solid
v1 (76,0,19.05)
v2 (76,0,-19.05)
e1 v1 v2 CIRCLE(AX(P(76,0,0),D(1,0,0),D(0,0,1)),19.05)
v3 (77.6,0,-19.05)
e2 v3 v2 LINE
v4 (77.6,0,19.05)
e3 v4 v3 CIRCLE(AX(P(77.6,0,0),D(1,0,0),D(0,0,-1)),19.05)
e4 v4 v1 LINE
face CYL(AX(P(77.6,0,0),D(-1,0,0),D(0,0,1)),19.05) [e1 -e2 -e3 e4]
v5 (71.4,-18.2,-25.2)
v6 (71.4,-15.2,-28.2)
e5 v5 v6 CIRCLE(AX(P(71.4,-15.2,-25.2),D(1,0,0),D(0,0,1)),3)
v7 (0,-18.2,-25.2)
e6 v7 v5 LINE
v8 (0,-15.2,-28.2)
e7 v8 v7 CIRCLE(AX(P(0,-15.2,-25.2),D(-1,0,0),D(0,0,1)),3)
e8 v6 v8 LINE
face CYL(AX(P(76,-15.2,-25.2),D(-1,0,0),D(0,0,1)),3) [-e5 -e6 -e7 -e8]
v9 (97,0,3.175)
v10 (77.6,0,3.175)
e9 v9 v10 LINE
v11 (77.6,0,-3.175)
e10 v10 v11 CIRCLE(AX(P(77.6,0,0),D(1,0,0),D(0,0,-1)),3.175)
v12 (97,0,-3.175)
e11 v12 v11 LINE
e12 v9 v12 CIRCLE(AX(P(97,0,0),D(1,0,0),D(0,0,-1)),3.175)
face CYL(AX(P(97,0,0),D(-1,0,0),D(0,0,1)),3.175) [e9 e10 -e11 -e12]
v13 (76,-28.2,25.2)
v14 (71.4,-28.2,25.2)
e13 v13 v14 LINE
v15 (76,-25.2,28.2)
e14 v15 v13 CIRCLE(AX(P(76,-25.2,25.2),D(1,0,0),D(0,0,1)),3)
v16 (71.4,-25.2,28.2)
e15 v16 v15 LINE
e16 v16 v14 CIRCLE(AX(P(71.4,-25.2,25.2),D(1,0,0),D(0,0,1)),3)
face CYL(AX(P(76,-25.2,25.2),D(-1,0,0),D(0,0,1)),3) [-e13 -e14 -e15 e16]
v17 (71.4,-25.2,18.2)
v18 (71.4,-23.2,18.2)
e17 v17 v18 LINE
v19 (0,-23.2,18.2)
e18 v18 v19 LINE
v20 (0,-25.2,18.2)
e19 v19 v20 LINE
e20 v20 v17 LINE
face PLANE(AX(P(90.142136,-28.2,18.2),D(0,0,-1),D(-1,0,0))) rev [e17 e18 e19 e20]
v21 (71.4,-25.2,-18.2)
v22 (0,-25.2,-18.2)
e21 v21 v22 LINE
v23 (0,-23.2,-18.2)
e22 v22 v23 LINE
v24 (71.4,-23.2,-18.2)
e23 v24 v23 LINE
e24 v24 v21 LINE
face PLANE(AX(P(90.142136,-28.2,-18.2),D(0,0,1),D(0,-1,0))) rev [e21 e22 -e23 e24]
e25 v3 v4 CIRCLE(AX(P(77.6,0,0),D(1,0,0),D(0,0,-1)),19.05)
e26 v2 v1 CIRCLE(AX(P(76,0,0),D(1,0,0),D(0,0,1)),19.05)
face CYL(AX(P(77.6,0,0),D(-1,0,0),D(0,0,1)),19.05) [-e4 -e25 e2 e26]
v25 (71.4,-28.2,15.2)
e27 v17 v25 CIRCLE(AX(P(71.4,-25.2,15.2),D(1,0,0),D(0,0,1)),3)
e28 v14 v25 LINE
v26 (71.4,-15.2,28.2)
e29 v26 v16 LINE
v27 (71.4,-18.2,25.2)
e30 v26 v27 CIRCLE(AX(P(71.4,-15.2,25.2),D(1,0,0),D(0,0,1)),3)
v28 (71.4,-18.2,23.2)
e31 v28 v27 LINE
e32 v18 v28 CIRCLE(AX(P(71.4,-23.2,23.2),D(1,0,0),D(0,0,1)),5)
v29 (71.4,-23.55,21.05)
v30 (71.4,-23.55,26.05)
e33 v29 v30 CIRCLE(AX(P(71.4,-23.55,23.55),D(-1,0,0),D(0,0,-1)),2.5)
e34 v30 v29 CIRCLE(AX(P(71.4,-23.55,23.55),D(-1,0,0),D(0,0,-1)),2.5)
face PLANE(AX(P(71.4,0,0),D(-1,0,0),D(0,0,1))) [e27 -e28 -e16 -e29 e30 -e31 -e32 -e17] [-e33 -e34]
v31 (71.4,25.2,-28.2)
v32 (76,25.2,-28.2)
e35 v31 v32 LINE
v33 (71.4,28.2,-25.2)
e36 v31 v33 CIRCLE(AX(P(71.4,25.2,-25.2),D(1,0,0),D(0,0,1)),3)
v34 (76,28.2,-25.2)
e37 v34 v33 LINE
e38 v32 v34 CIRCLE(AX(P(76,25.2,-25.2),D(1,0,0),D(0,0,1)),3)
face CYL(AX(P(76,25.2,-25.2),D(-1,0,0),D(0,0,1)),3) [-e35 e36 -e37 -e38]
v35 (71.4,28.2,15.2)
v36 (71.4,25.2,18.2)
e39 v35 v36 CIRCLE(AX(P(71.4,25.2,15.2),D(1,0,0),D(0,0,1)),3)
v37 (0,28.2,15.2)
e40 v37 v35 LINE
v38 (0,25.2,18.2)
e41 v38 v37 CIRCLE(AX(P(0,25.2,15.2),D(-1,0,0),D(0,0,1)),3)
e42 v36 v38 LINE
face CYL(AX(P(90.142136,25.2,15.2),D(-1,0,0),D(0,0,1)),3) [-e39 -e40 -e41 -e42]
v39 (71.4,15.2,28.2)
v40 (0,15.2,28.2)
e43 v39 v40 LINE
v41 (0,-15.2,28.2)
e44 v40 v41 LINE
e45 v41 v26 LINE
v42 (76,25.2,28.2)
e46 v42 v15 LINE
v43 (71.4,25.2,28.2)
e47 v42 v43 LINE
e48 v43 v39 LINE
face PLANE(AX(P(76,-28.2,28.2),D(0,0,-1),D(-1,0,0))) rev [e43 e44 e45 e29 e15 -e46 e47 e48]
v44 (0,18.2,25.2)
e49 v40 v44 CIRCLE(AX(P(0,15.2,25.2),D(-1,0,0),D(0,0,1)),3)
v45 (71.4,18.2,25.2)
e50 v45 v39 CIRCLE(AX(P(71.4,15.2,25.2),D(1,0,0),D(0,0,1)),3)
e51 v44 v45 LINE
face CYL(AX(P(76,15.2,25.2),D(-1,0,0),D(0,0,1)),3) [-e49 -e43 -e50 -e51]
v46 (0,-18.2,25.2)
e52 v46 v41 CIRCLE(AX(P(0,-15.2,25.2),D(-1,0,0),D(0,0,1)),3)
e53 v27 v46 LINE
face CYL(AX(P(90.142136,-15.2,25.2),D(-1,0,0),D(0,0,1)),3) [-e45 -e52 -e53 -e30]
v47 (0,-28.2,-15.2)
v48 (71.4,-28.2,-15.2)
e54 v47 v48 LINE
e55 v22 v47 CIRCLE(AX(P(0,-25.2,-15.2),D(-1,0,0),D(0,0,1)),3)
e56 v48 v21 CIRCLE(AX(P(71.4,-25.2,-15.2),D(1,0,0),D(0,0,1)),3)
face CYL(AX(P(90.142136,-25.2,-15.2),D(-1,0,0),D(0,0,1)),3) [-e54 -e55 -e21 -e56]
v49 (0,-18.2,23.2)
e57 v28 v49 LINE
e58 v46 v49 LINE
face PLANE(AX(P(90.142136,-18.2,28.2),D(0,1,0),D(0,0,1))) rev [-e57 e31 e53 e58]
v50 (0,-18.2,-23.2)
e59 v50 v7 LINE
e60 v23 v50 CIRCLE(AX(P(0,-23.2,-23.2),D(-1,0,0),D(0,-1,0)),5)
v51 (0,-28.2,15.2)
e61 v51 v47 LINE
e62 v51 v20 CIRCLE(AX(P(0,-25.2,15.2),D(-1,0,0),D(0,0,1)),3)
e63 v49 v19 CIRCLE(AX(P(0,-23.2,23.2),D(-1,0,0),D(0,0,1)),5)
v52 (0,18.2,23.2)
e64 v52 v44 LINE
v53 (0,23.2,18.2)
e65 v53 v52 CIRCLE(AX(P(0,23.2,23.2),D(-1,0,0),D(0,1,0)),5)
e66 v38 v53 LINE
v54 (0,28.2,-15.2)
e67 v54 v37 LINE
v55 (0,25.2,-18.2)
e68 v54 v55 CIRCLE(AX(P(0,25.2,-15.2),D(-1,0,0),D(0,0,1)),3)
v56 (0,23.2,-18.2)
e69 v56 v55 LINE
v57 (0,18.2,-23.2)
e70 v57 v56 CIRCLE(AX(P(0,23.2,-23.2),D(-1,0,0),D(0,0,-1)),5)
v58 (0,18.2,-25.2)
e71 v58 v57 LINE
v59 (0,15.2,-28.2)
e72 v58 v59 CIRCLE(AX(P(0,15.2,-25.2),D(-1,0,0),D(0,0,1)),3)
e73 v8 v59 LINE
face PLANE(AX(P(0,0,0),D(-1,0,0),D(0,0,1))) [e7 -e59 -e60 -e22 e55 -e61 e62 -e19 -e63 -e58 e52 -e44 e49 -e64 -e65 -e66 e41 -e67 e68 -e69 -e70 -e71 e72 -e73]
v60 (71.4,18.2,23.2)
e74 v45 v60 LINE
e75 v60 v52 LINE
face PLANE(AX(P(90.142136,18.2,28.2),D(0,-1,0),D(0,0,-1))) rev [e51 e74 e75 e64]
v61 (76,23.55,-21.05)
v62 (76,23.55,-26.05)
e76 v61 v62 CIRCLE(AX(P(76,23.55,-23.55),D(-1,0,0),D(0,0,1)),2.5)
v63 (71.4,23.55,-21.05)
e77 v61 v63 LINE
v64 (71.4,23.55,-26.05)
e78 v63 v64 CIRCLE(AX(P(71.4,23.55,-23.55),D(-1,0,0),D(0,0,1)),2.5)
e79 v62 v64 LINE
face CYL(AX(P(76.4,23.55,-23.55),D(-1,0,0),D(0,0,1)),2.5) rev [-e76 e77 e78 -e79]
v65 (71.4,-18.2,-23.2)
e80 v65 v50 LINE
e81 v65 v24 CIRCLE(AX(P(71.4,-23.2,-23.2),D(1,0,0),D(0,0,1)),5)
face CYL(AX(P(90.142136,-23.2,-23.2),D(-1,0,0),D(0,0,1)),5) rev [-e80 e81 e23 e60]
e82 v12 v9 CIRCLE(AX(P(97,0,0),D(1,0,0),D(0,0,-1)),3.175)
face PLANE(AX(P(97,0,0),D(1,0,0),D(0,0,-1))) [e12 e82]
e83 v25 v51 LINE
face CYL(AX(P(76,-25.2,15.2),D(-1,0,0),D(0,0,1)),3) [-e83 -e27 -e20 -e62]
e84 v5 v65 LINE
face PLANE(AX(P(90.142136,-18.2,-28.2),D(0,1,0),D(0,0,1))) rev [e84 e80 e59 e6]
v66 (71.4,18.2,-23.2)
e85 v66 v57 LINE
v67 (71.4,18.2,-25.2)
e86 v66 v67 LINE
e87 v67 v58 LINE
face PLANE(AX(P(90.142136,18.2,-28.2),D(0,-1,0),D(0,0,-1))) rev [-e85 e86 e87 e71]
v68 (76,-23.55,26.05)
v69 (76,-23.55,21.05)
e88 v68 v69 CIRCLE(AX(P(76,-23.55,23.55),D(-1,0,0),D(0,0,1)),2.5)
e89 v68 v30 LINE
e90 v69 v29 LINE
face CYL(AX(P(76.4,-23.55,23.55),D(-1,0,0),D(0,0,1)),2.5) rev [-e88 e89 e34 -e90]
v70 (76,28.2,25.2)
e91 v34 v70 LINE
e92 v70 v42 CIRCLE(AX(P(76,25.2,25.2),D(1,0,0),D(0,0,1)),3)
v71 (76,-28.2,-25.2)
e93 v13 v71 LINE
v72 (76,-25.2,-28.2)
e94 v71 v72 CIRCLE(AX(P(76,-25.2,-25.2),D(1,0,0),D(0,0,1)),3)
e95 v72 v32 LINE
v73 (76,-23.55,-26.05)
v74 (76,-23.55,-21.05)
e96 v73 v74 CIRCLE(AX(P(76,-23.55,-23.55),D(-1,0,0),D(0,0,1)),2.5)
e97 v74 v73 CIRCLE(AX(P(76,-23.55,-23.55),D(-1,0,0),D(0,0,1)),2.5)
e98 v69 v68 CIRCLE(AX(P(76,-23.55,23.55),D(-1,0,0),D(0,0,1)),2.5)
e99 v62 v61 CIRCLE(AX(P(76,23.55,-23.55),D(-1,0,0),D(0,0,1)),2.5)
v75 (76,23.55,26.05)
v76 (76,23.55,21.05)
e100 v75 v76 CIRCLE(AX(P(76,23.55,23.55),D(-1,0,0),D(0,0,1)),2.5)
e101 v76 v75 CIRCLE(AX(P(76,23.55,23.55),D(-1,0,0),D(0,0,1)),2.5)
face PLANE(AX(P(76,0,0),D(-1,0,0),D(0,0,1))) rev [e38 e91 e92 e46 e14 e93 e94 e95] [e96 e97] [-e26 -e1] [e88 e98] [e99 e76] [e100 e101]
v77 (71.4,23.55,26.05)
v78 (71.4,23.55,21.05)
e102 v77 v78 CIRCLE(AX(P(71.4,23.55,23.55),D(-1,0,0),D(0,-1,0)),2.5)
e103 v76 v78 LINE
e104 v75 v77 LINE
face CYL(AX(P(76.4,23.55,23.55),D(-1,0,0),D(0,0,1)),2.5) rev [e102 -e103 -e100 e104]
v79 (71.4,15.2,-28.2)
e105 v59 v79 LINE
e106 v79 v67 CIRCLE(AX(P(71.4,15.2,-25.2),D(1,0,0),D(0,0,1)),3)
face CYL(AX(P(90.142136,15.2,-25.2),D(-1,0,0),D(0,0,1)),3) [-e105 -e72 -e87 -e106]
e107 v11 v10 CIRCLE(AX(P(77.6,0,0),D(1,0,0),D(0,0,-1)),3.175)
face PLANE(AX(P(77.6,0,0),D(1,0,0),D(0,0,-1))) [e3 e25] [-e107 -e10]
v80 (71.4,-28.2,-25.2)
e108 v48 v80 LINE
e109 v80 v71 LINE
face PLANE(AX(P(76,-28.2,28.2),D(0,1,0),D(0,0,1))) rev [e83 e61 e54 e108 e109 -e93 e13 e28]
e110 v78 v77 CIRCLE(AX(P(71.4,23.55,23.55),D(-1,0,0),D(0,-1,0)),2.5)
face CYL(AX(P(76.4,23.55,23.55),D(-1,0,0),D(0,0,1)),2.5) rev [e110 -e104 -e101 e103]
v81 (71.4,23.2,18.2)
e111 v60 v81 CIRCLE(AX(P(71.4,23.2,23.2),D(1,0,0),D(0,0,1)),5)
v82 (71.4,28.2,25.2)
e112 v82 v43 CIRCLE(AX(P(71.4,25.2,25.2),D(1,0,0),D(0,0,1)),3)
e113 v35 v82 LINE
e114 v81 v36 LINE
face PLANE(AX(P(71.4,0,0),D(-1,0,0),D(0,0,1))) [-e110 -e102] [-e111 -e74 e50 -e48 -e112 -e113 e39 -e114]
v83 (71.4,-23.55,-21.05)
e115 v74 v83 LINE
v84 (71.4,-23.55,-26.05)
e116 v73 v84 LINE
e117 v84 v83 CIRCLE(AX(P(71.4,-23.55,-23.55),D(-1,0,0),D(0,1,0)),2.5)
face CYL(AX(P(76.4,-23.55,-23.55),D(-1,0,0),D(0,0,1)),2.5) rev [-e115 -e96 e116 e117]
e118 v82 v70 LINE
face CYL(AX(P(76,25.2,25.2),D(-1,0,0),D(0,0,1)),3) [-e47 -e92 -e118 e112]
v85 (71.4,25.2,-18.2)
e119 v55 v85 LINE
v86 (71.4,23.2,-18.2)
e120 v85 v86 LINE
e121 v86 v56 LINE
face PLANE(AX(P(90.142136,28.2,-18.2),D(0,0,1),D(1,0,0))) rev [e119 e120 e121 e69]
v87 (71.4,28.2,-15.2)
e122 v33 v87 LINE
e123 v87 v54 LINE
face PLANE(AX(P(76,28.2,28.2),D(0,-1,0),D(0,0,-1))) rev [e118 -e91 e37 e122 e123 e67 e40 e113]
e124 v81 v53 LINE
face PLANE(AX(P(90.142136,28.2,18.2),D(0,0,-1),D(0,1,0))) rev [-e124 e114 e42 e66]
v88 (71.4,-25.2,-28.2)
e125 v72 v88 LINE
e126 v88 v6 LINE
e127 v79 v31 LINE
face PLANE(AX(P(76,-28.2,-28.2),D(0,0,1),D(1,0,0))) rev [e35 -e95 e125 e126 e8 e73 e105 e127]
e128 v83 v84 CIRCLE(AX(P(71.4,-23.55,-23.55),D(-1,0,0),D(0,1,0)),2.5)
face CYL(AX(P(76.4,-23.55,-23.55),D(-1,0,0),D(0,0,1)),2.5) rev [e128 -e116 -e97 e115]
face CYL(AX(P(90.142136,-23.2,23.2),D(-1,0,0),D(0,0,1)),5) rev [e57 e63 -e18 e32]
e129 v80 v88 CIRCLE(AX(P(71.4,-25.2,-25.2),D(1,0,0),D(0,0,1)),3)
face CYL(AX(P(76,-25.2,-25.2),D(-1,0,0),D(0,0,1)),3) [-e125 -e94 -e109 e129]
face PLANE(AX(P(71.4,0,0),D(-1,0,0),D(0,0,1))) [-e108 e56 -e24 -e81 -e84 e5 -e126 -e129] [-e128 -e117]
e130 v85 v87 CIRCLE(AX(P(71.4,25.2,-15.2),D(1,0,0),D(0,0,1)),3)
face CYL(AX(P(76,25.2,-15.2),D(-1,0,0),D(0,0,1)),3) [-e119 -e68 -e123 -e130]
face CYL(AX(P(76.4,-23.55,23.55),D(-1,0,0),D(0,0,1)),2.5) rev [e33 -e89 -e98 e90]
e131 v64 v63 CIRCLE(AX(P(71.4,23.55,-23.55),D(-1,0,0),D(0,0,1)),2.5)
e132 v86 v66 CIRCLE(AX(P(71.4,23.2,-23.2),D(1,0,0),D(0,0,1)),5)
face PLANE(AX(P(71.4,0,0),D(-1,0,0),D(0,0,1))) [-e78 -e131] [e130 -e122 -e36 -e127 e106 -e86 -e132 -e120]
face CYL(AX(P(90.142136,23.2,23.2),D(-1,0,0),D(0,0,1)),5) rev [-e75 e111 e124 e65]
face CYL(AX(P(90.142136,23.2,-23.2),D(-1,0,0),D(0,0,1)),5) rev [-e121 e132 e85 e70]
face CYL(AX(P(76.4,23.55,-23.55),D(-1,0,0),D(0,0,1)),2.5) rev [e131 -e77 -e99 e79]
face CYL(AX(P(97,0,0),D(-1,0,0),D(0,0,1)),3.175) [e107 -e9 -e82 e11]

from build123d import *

# Parameters (mm, degrees)
SKETCH_1_W               = 56.4
SKETCH_1_H               = 56.4
EXTRUDE_1_DEPTH          = 76
SKETCH_2_R               = 19.05
EXTRUDE_2_DEPTH          = 1.6
SKETCH_3_R               = 3.175
EXTRUDE_3_DEPTH          = 19.4
FILLET_1_R               = 3
CUT_EXTRUDE_1_DEPTH      = 71.4
SKETCH_5_R               = 2.5
CUT_EXTRUDE_2_DEPTH      = 5
PATTERN_CIRCULAR_3_COUNT = 4
FILLET_2_R               = 3


with BuildPart() as part:
    # 草图1 → 凸台-拉伸1 (new body)
    with BuildSketch(Plane(origin=(0, 0, 0), x_dir=(0, 0, -1), z_dir=(1, 0, 0))):
        Rectangle(SKETCH_1_W, SKETCH_1_H)
    extrude(amount=EXTRUDE_1_DEPTH)

    # 草图2 → 凸台-拉伸2 (add)
    with BuildSketch(Plane(origin=(76, 0, 0), x_dir=(0, 0, -1), z_dir=(1, 0, 0))):
        with Locations(Location((0, 0, 0), (0, 0, 180))):
            Circle(SKETCH_2_R)
    extrude(amount=EXTRUDE_2_DEPTH)

    # 草图3 → 凸台-拉伸3 (add)
    with BuildSketch(Plane(origin=(77.6, 0, 0), x_dir=(0, 0, -1), z_dir=(1, 0, 0))):
        Circle(SKETCH_3_R)
    extrude(amount=EXTRUDE_3_DEPTH)

    # 圆角1
    fillet_1_edges = [part.edges().sort_by_distance(p)[0] for p in [
        (38, -28.2, -28.2),
        (38, -28.2, 28.2),
        (38, 28.2, 28.2),
        (38, 28.2, -28.2),
    ]]
    fillet(fillet_1_edges, radius=FILLET_1_R)

    # 草图4 → 切除-拉伸1 (cut)
    with BuildSketch(Plane.ZY):
        with BuildLine():
            Line((-28.2, 28.2), (-18.2, 28.2))
            Line((-18.2, 28.2), (-18.2, 23.2))
            ThreePointArc((-18.2, 23.2), (-19.664466094, 19.664466094), (-23.2, 18.2))
            Line((-23.2, 18.2), (-28.2, 18.2))
            Line((-28.2, 18.2), (-28.2, 28.2))
        make_face()
    cut_extrude_1 = extrude(amount=-CUT_EXTRUDE_1_DEPTH, mode=Mode.SUBTRACT)

    # 草图5 → 切除-拉伸2 (cut)
    with BuildSketch(Plane.ZY.offset(-71.4)):
        with Locations((-23.55, 23.55)):
            Circle(SKETCH_5_R)
    cut_extrude_2 = extrude(amount=-CUT_EXTRUDE_2_DEPTH, mode=Mode.SUBTRACT)

    # 阵列(圆周)3: 切除-拉伸1, 切除-拉伸2 ×4 about axis
    pattern_circular_3_axis = Axis((0, 0, 0), (1, 0, 0))
    add([cut_extrude_1.rotate(pattern_circular_3_axis, i * 360 / PATTERN_CIRCULAR_3_COUNT) for i in range(1, PATTERN_CIRCULAR_3_COUNT)], mode=Mode.SUBTRACT)
    add([cut_extrude_2.rotate(pattern_circular_3_axis, i * 360 / PATTERN_CIRCULAR_3_COUNT) for i in range(1, PATTERN_CIRCULAR_3_COUNT)], mode=Mode.SUBTRACT)

    # 圆角2
    fillet_2_edges = [part.edges().sort_by_distance(p)[0] for p in [
        (35.7, 28.2, 18.2),
        (35.7, 18.2, 28.2),
        (35.7, 18.2, -28.2),
        (35.7, 28.2, -18.2),
        (35.7, -28.2, -18.2),
        (35.7, -18.2, -28.2),
        (35.7, -18.2, 28.2),
        (35.7, -28.2, 18.2),
    ]]
    fillet(fillet_2_edges, radius=FILLET_2_R)


solid = part.part
